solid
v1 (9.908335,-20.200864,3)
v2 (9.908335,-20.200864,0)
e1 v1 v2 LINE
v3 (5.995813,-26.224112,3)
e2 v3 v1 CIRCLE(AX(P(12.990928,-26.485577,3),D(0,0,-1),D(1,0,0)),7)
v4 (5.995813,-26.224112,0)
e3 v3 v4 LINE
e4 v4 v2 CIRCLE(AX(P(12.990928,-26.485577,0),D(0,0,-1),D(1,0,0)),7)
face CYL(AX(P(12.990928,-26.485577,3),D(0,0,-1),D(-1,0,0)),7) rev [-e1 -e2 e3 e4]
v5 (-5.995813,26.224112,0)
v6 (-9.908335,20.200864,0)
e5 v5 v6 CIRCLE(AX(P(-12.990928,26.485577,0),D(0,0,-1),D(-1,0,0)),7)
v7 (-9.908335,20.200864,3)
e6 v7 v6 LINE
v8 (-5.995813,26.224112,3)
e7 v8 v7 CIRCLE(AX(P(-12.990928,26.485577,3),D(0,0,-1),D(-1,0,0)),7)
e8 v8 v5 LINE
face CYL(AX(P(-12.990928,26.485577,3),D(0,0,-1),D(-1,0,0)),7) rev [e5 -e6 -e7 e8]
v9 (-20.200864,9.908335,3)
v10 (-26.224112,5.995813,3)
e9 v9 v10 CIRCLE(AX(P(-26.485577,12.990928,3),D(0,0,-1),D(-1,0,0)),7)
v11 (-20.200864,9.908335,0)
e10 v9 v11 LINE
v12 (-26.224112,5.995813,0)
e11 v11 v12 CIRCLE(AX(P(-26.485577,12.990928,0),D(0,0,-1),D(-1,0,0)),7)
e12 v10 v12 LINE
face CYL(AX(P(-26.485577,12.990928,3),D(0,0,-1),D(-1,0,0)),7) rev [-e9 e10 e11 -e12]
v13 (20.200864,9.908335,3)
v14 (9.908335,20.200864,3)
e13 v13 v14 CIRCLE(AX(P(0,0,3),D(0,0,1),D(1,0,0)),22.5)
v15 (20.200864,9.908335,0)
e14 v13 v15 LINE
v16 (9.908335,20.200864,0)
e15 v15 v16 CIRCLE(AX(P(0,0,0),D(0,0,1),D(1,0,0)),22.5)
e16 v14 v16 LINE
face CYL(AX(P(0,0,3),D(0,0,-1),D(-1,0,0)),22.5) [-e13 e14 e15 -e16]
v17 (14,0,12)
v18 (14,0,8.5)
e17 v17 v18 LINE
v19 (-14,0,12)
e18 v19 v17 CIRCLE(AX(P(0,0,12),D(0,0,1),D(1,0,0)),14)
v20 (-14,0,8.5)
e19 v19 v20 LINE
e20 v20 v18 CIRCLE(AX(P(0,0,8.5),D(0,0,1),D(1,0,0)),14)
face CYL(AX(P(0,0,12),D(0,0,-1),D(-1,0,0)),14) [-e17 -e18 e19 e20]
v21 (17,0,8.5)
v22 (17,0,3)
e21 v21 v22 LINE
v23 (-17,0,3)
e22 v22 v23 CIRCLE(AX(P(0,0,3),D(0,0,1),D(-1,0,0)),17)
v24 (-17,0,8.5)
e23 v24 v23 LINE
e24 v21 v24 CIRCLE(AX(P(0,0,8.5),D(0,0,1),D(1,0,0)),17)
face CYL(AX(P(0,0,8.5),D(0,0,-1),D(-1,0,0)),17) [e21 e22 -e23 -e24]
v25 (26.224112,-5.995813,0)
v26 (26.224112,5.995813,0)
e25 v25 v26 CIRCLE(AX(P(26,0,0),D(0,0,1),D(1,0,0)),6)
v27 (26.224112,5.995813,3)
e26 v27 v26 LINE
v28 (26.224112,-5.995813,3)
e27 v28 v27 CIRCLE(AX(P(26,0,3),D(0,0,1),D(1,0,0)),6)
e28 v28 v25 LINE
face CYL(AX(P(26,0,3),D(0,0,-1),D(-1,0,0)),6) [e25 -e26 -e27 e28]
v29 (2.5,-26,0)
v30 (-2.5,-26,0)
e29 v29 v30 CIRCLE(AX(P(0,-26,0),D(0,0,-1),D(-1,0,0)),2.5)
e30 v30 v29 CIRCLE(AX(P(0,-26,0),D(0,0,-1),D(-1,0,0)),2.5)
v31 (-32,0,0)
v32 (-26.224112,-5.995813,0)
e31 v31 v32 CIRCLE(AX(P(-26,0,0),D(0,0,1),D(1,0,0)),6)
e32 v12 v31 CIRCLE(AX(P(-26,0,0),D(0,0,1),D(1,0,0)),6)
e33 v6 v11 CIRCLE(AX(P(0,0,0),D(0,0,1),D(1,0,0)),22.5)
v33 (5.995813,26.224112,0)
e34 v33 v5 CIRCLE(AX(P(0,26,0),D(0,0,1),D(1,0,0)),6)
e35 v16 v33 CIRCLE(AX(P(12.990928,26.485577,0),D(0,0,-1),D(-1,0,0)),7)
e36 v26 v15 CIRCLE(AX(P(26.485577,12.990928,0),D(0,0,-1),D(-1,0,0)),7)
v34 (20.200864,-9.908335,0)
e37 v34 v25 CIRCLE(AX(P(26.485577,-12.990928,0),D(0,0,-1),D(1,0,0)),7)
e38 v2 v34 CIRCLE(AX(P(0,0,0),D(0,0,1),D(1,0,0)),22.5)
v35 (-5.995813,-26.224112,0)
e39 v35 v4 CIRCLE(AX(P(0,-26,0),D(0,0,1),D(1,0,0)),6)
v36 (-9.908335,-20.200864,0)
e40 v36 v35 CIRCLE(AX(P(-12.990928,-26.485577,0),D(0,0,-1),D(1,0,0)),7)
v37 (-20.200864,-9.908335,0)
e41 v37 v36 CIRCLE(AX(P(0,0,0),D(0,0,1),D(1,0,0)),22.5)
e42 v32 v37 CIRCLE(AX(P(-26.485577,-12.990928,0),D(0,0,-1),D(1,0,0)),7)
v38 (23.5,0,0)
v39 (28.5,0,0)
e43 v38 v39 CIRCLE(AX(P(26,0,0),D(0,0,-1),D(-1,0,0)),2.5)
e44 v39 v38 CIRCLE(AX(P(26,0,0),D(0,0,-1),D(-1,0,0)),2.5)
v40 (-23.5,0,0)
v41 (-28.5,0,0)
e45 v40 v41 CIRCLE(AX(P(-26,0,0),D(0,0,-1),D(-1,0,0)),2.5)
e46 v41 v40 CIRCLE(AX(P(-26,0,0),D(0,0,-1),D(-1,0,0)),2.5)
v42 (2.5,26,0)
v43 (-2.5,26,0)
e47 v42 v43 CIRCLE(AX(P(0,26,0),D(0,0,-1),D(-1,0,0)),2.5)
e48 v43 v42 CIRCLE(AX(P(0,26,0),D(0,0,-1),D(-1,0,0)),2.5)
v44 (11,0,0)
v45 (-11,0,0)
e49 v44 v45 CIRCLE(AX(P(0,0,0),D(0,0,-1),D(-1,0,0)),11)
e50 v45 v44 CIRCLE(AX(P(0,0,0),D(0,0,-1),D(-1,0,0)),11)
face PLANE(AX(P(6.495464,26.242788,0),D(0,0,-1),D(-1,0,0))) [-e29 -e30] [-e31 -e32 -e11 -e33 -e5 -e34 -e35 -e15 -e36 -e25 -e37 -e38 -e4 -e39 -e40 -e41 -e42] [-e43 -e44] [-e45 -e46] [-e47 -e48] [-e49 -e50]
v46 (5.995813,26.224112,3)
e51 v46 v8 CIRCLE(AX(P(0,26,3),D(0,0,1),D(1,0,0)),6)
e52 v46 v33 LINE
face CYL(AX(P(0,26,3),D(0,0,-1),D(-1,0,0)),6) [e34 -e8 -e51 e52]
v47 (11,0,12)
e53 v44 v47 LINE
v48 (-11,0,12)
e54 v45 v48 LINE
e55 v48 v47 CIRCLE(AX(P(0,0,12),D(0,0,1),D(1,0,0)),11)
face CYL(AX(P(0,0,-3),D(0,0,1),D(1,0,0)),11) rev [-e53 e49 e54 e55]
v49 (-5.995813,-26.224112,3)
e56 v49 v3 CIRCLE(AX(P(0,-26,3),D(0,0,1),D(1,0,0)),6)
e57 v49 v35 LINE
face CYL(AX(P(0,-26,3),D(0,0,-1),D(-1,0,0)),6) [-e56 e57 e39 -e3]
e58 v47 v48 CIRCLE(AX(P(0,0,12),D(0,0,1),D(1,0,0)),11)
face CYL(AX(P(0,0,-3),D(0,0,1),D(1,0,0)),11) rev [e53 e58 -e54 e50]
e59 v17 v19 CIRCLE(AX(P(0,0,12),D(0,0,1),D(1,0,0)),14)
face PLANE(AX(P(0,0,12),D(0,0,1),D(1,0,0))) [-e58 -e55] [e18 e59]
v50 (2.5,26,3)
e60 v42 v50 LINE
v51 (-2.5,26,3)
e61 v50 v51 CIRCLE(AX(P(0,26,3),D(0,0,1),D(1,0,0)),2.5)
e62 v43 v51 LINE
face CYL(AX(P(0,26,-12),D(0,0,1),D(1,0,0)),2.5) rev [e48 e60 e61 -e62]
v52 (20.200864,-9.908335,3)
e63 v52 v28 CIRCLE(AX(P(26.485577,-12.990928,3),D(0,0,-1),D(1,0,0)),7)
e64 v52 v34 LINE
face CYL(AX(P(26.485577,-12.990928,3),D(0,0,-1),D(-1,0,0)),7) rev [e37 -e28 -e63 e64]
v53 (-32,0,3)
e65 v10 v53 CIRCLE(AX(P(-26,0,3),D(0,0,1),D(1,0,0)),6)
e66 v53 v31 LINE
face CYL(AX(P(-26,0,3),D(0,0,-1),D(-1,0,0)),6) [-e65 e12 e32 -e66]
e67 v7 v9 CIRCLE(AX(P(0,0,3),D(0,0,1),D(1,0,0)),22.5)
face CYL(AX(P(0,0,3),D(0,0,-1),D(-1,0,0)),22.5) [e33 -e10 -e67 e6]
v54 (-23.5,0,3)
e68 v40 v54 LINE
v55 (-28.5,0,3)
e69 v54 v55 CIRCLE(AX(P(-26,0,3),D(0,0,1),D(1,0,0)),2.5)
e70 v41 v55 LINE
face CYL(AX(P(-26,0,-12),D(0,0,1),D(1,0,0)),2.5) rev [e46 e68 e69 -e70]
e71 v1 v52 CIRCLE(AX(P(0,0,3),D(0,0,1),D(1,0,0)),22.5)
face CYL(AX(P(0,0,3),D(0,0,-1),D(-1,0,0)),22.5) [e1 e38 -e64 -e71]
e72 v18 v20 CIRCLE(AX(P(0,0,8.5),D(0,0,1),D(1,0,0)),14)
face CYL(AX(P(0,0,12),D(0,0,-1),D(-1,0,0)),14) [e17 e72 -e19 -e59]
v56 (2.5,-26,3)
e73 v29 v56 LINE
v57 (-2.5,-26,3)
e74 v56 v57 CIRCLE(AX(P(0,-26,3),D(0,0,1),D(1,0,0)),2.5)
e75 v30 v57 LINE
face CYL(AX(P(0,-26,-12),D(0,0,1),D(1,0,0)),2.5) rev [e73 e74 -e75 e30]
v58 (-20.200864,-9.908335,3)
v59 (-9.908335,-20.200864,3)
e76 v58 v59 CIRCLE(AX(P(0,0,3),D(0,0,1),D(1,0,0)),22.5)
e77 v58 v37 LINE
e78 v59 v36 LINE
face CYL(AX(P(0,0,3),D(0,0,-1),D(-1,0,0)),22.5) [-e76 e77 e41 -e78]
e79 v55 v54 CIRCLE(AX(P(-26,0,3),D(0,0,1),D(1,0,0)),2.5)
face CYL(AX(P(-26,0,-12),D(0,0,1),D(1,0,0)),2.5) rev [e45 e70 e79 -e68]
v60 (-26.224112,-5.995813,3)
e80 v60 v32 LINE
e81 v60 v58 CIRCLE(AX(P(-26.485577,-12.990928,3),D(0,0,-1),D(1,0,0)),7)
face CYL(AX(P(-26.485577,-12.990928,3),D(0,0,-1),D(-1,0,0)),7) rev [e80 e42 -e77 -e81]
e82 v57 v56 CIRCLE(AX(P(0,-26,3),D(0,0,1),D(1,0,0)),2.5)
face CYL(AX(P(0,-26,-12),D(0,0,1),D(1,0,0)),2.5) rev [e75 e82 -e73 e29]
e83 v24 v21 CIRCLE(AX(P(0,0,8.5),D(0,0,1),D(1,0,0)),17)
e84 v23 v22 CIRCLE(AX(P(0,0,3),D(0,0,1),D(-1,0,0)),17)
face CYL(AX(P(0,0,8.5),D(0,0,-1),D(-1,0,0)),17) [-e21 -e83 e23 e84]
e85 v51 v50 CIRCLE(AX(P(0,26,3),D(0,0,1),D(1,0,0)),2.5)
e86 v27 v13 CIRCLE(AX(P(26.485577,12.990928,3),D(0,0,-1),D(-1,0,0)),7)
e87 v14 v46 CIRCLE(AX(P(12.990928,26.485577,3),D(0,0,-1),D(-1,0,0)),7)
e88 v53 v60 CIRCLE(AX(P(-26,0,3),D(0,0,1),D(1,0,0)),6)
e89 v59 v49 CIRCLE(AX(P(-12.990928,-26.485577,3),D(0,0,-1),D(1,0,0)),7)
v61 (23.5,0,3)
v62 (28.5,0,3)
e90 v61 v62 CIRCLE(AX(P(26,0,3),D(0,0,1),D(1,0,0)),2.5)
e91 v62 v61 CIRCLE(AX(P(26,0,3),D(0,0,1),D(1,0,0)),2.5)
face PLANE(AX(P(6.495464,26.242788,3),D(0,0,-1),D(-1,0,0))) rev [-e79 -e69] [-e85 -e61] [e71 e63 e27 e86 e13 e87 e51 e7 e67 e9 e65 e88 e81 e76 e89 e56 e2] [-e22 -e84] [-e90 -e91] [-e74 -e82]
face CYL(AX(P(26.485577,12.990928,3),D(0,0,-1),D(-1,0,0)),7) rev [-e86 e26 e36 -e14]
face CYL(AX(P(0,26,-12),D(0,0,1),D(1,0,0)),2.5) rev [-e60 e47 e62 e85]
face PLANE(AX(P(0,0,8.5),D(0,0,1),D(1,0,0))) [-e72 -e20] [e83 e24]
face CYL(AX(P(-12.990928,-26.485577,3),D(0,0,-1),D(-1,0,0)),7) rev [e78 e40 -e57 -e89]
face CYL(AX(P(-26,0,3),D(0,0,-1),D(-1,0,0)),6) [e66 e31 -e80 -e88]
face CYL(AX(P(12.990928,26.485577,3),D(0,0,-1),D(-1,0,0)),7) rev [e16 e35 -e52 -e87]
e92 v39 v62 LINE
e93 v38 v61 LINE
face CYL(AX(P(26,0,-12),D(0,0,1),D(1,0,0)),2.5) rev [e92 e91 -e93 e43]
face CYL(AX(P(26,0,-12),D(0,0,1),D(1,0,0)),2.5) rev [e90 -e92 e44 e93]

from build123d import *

# Parameters (mm, degrees)
LUG_FLANGE_DEPTH            = 3
HUB_SKETCH_R                = 17
HUB_BOSS_DEPTH              = 5.5
SPIGOT_SKETCH_R             = 14
LOCATING_SPIGOT_DEPTH       = 3.5
BEARING_BORE_SKETCH_R       = 11
BEARING_BORE_DEPTH          = 15
LUG_HOLES_SKETCH_R          = 2.5
LUG_MOUNTING_HOLES_4X_DEPTH = 15


with BuildPart() as part:
    # Flange Profile Sketch → Lug Flange (new body)
    with BuildSketch(Plane.XY):
        with BuildLine():
            ThreePointArc((9.908335055, -20.200863755), (15.909902577, -15.909902577), (20.200863755, -9.908335055))
            ThreePointArc((20.200863755, -9.908335055), (22.672432853, -7.120669901), (26.224112426, -5.995813007))
            ThreePointArc((26.224112426, -5.995813007), (32, 0), (26.224112426, 5.995813007))
            ThreePointArc((26.224112426, 5.995813007), (22.672432853, 7.120669901), (20.200863755, 9.908335055))
            ThreePointArc((20.200863755, 9.908335055), (15.909902577, 15.909902577), (9.908335055, 20.200863755))
            ThreePointArc((9.908335055, 20.200863755), (7.120669901, 22.672432853), (5.995813007, 26.224112426))
            ThreePointArc((5.995813007, 26.224112426), (0, 32), (-5.995813007, 26.224112426))
            ThreePointArc((-5.995813007, 26.224112426), (-7.120669901, 22.672432853), (-9.908335055, 20.200863755))
            ThreePointArc((-9.908335055, 20.200863755), (-15.909902577, 15.909902577), (-20.200863755, 9.908335055))
            ThreePointArc((-20.200863755, 9.908335055), (-22.672432853, 7.120669901), (-26.224112426, 5.995813007))
            ThreePointArc((-26.224112426, 5.995813007), (-32, 0), (-26.224112426, -5.995813007))
            ThreePointArc((-26.224112426, -5.995813007), (-22.672432853, -7.120669901), (-20.200863755, -9.908335055))
            ThreePointArc((-20.200863755, -9.908335055), (-15.909902577, -15.909902577), (-9.908335055, -20.200863755))
            ThreePointArc((-9.908335055, -20.200863755), (-7.120669901, -22.672432853), (-5.995813007, -26.224112426))
            ThreePointArc((-5.995813007, -26.224112426), (0, -32), (5.995813007, -26.224112426))
            ThreePointArc((5.995813007, -26.224112426), (7.120669901, -22.672432853), (9.908335055, -20.200863755))
        make_face()
    extrude(amount=LUG_FLANGE_DEPTH)

    # Hub Sketch → Hub Boss (add)
    with BuildSketch(Plane.XY.offset(3)):
        with Locations(Location((0, 0, 0), (0, 0, 180))):
            Circle(HUB_SKETCH_R)
    extrude(amount=HUB_BOSS_DEPTH)

    # Spigot Sketch → Locating Spigot (add)
    with BuildSketch(Plane.XY.offset(8.5)):
        Circle(SPIGOT_SKETCH_R)
    extrude(amount=LOCATING_SPIGOT_DEPTH)

    # Bearing Bore Sketch → Bearing Bore (cut)
    with BuildSketch(Plane.XY.offset(12)):
        Circle(BEARING_BORE_SKETCH_R)
    extrude(amount=-BEARING_BORE_DEPTH, mode=Mode.SUBTRACT)

    # Lug Holes Sketch → Lug Mounting Holes 4x (cut)
    with BuildSketch(Plane.XY.offset(3)):
        with Locations((-26, 0)):
            Circle(LUG_HOLES_SKETCH_R)
        with Locations((0, 26)):
            Circle(LUG_HOLES_SKETCH_R)
        with Locations((26, 0)):
            Circle(LUG_HOLES_SKETCH_R)
        with Locations((0, -26)):
            Circle(LUG_HOLES_SKETCH_R)
    extrude(amount=-LUG_MOUNTING_HOLES_4X_DEPTH, mode=Mode.SUBTRACT)


solid = part.part
